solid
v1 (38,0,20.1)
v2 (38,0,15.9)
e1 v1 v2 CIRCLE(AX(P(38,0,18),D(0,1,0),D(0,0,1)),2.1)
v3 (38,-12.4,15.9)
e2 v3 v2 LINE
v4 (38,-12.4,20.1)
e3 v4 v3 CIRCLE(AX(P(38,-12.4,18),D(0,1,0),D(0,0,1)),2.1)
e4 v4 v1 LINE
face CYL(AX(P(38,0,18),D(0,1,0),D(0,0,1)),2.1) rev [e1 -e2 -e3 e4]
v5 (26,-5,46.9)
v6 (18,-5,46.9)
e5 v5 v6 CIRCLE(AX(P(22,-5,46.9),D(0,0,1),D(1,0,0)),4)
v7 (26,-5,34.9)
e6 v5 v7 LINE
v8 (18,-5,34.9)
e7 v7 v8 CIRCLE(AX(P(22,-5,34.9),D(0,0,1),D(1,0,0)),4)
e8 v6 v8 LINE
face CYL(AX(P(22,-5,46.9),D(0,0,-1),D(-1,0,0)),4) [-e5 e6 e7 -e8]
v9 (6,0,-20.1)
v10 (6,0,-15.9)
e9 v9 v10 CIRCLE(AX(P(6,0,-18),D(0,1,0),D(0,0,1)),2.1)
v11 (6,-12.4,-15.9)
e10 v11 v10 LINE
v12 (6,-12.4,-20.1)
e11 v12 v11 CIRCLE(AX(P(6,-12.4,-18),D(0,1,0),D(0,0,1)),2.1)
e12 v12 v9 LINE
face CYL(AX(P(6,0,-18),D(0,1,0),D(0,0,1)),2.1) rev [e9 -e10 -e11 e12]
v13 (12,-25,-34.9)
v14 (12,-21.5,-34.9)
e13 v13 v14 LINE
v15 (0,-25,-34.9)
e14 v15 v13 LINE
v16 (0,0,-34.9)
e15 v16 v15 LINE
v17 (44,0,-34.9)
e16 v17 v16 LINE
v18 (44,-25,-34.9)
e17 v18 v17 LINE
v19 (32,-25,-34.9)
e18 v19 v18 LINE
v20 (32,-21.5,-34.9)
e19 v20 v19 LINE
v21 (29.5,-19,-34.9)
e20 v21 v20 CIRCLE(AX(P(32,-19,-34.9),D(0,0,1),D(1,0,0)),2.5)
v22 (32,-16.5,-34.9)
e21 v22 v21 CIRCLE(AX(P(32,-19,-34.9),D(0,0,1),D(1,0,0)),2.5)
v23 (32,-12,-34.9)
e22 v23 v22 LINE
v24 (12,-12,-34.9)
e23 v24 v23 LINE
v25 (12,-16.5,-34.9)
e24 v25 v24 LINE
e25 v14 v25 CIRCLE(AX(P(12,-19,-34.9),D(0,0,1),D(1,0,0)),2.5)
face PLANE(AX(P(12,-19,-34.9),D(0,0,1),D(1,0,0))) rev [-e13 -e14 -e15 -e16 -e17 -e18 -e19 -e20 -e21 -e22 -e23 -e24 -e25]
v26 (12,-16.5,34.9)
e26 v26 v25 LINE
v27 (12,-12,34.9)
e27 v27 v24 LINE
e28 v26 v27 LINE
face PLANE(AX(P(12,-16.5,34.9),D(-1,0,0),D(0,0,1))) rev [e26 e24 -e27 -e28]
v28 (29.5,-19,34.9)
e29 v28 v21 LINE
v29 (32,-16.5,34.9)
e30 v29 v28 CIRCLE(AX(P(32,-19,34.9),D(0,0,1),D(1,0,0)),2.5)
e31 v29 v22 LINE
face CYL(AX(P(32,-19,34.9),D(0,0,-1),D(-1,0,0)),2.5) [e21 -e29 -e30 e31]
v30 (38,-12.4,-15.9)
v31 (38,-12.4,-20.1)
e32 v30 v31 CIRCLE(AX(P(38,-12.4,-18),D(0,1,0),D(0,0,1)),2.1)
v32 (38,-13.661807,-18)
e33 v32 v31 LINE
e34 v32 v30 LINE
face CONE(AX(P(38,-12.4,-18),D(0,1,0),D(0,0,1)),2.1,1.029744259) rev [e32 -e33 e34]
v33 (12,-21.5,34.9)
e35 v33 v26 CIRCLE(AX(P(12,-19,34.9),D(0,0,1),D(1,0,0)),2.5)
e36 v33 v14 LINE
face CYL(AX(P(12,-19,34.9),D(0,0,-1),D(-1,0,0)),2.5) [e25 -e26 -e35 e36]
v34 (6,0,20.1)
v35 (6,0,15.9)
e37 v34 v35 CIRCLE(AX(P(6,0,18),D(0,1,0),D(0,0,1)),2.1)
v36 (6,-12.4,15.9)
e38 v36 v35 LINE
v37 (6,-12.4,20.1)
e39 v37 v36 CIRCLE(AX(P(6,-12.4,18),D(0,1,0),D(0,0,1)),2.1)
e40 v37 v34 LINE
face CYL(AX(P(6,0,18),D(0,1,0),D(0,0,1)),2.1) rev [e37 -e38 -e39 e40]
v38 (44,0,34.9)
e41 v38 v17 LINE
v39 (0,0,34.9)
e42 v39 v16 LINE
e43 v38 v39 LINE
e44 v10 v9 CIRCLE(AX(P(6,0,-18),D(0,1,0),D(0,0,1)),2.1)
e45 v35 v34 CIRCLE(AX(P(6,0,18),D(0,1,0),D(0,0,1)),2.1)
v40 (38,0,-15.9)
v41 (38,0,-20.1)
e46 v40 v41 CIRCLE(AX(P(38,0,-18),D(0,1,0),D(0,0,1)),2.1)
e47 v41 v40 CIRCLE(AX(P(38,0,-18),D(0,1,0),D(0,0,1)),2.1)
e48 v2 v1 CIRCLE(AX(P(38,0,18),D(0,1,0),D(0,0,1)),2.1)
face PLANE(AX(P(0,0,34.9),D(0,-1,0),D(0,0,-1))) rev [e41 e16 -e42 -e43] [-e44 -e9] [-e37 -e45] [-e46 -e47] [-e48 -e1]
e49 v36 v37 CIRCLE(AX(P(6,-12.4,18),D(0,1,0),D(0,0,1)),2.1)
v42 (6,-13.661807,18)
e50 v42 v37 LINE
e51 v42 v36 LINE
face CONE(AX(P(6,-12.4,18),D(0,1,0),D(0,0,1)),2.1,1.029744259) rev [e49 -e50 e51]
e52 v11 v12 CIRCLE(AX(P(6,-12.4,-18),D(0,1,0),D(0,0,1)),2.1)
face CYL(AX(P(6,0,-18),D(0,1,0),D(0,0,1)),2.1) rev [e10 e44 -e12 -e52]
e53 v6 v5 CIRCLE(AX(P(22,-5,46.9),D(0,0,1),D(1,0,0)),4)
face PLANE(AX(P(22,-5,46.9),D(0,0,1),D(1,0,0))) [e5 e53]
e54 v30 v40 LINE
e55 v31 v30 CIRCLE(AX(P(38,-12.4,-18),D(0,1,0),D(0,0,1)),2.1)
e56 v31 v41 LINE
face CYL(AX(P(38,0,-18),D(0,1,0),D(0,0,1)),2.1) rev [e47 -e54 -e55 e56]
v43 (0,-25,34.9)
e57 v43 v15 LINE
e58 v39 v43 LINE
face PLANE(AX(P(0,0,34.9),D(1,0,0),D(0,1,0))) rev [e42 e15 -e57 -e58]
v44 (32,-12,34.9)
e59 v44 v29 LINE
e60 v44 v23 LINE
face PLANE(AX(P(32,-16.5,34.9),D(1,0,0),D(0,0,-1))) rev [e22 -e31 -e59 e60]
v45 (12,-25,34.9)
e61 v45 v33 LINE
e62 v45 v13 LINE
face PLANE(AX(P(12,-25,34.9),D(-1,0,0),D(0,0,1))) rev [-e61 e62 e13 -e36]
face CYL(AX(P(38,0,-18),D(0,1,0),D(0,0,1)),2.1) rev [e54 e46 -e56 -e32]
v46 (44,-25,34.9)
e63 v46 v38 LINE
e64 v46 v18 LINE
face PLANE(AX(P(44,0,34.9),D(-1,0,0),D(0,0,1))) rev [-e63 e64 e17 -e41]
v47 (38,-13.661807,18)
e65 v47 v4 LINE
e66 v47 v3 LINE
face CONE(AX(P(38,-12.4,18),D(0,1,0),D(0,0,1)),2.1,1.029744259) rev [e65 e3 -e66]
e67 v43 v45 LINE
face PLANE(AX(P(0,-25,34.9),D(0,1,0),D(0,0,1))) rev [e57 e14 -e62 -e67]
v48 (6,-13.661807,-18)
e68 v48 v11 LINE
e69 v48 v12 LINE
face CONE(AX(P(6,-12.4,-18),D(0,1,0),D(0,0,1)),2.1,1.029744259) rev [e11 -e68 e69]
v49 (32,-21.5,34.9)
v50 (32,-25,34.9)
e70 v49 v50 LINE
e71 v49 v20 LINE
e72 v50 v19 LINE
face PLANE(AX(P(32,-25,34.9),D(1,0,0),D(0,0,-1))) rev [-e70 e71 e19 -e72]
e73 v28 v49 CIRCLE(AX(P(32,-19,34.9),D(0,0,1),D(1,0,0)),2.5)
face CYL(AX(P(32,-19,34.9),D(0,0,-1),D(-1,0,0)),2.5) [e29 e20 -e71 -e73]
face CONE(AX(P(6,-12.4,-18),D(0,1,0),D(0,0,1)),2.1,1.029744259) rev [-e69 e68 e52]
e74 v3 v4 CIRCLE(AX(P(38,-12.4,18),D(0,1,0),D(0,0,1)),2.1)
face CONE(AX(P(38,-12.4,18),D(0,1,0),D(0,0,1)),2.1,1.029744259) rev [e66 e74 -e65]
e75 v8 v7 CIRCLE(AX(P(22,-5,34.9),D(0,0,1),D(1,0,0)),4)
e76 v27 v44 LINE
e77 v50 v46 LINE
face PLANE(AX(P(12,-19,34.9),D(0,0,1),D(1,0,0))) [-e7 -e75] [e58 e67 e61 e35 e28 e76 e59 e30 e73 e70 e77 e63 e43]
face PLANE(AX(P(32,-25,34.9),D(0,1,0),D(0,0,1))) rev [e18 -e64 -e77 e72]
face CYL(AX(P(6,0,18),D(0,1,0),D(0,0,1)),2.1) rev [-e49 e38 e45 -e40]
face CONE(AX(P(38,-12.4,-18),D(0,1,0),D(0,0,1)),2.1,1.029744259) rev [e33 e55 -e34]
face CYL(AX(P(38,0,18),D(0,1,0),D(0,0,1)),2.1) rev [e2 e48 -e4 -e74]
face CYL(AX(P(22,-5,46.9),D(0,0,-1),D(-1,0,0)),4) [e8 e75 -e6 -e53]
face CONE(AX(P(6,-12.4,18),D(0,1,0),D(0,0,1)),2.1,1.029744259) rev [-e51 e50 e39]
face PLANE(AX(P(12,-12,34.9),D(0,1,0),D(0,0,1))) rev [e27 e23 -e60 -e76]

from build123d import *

# Parameters (mm, degrees)
EXTRUDE1_DEPTH        = 34.9
SKETCH2_R             = 4
EXTRUDE2_DEPTH        = 12
M5_TAPPED_HOLE1_D     = 4.2
M5_TAPPED_HOLE1_DEPTH = 12.4
M5_TAPPED_HOLE1_TIP   = 1.2618073


with BuildPart() as part:
    # Sketch1 → Extrude1 (new, symmetric)
    with BuildSketch(Plane.XY):
        with BuildLine():
            Line((32, -25), (44, -25))
            Line((44, -25), (44, 0))
            Line((44, 0), (0, 0))
            Line((0, 0), (0, -25))
            Line((0, -25), (12, -25))
            Line((12, -25), (12, -21.5))
            ThreePointArc((12, -21.5), (14.5, -19), (12, -16.5))
            Line((12, -16.5), (12, -12))
            Line((12, -12), (32, -12))
            Line((32, -12), (32, -16.5))
            ThreePointArc((32, -16.5), (29.5, -19), (32, -21.5))
            Line((32, -21.5), (32, -25))
        make_face()
    extrude(amount=EXTRUDE1_DEPTH, both=True)

    # Sketch2 → Extrude2 (add)
    with BuildSketch(Plane.XY.offset(34.9)):
        with Locations((22, -5)):
            Circle(SKETCH2_R)
    extrude(amount=EXTRUDE2_DEPTH)

    # M5 Tapped Hole1
    with Locations(Plane(origin=(6, 0, 18), x_dir=(0, 0, 1), z_dir=(0, 1, 0))):
        with Locations((0, 0), (0, 32), (-36, 0), (-36, 32)):
            Hole(M5_TAPPED_HOLE1_D / 2, depth=M5_TAPPED_HOLE1_DEPTH)
            with Locations((0, 0, -(M5_TAPPED_HOLE1_DEPTH + M5_TAPPED_HOLE1_TIP / 2))):  # 118° drill point
                Cone(0, M5_TAPPED_HOLE1_D / 2, M5_TAPPED_HOLE1_TIP, mode=Mode.SUBTRACT)


solid = part.part
